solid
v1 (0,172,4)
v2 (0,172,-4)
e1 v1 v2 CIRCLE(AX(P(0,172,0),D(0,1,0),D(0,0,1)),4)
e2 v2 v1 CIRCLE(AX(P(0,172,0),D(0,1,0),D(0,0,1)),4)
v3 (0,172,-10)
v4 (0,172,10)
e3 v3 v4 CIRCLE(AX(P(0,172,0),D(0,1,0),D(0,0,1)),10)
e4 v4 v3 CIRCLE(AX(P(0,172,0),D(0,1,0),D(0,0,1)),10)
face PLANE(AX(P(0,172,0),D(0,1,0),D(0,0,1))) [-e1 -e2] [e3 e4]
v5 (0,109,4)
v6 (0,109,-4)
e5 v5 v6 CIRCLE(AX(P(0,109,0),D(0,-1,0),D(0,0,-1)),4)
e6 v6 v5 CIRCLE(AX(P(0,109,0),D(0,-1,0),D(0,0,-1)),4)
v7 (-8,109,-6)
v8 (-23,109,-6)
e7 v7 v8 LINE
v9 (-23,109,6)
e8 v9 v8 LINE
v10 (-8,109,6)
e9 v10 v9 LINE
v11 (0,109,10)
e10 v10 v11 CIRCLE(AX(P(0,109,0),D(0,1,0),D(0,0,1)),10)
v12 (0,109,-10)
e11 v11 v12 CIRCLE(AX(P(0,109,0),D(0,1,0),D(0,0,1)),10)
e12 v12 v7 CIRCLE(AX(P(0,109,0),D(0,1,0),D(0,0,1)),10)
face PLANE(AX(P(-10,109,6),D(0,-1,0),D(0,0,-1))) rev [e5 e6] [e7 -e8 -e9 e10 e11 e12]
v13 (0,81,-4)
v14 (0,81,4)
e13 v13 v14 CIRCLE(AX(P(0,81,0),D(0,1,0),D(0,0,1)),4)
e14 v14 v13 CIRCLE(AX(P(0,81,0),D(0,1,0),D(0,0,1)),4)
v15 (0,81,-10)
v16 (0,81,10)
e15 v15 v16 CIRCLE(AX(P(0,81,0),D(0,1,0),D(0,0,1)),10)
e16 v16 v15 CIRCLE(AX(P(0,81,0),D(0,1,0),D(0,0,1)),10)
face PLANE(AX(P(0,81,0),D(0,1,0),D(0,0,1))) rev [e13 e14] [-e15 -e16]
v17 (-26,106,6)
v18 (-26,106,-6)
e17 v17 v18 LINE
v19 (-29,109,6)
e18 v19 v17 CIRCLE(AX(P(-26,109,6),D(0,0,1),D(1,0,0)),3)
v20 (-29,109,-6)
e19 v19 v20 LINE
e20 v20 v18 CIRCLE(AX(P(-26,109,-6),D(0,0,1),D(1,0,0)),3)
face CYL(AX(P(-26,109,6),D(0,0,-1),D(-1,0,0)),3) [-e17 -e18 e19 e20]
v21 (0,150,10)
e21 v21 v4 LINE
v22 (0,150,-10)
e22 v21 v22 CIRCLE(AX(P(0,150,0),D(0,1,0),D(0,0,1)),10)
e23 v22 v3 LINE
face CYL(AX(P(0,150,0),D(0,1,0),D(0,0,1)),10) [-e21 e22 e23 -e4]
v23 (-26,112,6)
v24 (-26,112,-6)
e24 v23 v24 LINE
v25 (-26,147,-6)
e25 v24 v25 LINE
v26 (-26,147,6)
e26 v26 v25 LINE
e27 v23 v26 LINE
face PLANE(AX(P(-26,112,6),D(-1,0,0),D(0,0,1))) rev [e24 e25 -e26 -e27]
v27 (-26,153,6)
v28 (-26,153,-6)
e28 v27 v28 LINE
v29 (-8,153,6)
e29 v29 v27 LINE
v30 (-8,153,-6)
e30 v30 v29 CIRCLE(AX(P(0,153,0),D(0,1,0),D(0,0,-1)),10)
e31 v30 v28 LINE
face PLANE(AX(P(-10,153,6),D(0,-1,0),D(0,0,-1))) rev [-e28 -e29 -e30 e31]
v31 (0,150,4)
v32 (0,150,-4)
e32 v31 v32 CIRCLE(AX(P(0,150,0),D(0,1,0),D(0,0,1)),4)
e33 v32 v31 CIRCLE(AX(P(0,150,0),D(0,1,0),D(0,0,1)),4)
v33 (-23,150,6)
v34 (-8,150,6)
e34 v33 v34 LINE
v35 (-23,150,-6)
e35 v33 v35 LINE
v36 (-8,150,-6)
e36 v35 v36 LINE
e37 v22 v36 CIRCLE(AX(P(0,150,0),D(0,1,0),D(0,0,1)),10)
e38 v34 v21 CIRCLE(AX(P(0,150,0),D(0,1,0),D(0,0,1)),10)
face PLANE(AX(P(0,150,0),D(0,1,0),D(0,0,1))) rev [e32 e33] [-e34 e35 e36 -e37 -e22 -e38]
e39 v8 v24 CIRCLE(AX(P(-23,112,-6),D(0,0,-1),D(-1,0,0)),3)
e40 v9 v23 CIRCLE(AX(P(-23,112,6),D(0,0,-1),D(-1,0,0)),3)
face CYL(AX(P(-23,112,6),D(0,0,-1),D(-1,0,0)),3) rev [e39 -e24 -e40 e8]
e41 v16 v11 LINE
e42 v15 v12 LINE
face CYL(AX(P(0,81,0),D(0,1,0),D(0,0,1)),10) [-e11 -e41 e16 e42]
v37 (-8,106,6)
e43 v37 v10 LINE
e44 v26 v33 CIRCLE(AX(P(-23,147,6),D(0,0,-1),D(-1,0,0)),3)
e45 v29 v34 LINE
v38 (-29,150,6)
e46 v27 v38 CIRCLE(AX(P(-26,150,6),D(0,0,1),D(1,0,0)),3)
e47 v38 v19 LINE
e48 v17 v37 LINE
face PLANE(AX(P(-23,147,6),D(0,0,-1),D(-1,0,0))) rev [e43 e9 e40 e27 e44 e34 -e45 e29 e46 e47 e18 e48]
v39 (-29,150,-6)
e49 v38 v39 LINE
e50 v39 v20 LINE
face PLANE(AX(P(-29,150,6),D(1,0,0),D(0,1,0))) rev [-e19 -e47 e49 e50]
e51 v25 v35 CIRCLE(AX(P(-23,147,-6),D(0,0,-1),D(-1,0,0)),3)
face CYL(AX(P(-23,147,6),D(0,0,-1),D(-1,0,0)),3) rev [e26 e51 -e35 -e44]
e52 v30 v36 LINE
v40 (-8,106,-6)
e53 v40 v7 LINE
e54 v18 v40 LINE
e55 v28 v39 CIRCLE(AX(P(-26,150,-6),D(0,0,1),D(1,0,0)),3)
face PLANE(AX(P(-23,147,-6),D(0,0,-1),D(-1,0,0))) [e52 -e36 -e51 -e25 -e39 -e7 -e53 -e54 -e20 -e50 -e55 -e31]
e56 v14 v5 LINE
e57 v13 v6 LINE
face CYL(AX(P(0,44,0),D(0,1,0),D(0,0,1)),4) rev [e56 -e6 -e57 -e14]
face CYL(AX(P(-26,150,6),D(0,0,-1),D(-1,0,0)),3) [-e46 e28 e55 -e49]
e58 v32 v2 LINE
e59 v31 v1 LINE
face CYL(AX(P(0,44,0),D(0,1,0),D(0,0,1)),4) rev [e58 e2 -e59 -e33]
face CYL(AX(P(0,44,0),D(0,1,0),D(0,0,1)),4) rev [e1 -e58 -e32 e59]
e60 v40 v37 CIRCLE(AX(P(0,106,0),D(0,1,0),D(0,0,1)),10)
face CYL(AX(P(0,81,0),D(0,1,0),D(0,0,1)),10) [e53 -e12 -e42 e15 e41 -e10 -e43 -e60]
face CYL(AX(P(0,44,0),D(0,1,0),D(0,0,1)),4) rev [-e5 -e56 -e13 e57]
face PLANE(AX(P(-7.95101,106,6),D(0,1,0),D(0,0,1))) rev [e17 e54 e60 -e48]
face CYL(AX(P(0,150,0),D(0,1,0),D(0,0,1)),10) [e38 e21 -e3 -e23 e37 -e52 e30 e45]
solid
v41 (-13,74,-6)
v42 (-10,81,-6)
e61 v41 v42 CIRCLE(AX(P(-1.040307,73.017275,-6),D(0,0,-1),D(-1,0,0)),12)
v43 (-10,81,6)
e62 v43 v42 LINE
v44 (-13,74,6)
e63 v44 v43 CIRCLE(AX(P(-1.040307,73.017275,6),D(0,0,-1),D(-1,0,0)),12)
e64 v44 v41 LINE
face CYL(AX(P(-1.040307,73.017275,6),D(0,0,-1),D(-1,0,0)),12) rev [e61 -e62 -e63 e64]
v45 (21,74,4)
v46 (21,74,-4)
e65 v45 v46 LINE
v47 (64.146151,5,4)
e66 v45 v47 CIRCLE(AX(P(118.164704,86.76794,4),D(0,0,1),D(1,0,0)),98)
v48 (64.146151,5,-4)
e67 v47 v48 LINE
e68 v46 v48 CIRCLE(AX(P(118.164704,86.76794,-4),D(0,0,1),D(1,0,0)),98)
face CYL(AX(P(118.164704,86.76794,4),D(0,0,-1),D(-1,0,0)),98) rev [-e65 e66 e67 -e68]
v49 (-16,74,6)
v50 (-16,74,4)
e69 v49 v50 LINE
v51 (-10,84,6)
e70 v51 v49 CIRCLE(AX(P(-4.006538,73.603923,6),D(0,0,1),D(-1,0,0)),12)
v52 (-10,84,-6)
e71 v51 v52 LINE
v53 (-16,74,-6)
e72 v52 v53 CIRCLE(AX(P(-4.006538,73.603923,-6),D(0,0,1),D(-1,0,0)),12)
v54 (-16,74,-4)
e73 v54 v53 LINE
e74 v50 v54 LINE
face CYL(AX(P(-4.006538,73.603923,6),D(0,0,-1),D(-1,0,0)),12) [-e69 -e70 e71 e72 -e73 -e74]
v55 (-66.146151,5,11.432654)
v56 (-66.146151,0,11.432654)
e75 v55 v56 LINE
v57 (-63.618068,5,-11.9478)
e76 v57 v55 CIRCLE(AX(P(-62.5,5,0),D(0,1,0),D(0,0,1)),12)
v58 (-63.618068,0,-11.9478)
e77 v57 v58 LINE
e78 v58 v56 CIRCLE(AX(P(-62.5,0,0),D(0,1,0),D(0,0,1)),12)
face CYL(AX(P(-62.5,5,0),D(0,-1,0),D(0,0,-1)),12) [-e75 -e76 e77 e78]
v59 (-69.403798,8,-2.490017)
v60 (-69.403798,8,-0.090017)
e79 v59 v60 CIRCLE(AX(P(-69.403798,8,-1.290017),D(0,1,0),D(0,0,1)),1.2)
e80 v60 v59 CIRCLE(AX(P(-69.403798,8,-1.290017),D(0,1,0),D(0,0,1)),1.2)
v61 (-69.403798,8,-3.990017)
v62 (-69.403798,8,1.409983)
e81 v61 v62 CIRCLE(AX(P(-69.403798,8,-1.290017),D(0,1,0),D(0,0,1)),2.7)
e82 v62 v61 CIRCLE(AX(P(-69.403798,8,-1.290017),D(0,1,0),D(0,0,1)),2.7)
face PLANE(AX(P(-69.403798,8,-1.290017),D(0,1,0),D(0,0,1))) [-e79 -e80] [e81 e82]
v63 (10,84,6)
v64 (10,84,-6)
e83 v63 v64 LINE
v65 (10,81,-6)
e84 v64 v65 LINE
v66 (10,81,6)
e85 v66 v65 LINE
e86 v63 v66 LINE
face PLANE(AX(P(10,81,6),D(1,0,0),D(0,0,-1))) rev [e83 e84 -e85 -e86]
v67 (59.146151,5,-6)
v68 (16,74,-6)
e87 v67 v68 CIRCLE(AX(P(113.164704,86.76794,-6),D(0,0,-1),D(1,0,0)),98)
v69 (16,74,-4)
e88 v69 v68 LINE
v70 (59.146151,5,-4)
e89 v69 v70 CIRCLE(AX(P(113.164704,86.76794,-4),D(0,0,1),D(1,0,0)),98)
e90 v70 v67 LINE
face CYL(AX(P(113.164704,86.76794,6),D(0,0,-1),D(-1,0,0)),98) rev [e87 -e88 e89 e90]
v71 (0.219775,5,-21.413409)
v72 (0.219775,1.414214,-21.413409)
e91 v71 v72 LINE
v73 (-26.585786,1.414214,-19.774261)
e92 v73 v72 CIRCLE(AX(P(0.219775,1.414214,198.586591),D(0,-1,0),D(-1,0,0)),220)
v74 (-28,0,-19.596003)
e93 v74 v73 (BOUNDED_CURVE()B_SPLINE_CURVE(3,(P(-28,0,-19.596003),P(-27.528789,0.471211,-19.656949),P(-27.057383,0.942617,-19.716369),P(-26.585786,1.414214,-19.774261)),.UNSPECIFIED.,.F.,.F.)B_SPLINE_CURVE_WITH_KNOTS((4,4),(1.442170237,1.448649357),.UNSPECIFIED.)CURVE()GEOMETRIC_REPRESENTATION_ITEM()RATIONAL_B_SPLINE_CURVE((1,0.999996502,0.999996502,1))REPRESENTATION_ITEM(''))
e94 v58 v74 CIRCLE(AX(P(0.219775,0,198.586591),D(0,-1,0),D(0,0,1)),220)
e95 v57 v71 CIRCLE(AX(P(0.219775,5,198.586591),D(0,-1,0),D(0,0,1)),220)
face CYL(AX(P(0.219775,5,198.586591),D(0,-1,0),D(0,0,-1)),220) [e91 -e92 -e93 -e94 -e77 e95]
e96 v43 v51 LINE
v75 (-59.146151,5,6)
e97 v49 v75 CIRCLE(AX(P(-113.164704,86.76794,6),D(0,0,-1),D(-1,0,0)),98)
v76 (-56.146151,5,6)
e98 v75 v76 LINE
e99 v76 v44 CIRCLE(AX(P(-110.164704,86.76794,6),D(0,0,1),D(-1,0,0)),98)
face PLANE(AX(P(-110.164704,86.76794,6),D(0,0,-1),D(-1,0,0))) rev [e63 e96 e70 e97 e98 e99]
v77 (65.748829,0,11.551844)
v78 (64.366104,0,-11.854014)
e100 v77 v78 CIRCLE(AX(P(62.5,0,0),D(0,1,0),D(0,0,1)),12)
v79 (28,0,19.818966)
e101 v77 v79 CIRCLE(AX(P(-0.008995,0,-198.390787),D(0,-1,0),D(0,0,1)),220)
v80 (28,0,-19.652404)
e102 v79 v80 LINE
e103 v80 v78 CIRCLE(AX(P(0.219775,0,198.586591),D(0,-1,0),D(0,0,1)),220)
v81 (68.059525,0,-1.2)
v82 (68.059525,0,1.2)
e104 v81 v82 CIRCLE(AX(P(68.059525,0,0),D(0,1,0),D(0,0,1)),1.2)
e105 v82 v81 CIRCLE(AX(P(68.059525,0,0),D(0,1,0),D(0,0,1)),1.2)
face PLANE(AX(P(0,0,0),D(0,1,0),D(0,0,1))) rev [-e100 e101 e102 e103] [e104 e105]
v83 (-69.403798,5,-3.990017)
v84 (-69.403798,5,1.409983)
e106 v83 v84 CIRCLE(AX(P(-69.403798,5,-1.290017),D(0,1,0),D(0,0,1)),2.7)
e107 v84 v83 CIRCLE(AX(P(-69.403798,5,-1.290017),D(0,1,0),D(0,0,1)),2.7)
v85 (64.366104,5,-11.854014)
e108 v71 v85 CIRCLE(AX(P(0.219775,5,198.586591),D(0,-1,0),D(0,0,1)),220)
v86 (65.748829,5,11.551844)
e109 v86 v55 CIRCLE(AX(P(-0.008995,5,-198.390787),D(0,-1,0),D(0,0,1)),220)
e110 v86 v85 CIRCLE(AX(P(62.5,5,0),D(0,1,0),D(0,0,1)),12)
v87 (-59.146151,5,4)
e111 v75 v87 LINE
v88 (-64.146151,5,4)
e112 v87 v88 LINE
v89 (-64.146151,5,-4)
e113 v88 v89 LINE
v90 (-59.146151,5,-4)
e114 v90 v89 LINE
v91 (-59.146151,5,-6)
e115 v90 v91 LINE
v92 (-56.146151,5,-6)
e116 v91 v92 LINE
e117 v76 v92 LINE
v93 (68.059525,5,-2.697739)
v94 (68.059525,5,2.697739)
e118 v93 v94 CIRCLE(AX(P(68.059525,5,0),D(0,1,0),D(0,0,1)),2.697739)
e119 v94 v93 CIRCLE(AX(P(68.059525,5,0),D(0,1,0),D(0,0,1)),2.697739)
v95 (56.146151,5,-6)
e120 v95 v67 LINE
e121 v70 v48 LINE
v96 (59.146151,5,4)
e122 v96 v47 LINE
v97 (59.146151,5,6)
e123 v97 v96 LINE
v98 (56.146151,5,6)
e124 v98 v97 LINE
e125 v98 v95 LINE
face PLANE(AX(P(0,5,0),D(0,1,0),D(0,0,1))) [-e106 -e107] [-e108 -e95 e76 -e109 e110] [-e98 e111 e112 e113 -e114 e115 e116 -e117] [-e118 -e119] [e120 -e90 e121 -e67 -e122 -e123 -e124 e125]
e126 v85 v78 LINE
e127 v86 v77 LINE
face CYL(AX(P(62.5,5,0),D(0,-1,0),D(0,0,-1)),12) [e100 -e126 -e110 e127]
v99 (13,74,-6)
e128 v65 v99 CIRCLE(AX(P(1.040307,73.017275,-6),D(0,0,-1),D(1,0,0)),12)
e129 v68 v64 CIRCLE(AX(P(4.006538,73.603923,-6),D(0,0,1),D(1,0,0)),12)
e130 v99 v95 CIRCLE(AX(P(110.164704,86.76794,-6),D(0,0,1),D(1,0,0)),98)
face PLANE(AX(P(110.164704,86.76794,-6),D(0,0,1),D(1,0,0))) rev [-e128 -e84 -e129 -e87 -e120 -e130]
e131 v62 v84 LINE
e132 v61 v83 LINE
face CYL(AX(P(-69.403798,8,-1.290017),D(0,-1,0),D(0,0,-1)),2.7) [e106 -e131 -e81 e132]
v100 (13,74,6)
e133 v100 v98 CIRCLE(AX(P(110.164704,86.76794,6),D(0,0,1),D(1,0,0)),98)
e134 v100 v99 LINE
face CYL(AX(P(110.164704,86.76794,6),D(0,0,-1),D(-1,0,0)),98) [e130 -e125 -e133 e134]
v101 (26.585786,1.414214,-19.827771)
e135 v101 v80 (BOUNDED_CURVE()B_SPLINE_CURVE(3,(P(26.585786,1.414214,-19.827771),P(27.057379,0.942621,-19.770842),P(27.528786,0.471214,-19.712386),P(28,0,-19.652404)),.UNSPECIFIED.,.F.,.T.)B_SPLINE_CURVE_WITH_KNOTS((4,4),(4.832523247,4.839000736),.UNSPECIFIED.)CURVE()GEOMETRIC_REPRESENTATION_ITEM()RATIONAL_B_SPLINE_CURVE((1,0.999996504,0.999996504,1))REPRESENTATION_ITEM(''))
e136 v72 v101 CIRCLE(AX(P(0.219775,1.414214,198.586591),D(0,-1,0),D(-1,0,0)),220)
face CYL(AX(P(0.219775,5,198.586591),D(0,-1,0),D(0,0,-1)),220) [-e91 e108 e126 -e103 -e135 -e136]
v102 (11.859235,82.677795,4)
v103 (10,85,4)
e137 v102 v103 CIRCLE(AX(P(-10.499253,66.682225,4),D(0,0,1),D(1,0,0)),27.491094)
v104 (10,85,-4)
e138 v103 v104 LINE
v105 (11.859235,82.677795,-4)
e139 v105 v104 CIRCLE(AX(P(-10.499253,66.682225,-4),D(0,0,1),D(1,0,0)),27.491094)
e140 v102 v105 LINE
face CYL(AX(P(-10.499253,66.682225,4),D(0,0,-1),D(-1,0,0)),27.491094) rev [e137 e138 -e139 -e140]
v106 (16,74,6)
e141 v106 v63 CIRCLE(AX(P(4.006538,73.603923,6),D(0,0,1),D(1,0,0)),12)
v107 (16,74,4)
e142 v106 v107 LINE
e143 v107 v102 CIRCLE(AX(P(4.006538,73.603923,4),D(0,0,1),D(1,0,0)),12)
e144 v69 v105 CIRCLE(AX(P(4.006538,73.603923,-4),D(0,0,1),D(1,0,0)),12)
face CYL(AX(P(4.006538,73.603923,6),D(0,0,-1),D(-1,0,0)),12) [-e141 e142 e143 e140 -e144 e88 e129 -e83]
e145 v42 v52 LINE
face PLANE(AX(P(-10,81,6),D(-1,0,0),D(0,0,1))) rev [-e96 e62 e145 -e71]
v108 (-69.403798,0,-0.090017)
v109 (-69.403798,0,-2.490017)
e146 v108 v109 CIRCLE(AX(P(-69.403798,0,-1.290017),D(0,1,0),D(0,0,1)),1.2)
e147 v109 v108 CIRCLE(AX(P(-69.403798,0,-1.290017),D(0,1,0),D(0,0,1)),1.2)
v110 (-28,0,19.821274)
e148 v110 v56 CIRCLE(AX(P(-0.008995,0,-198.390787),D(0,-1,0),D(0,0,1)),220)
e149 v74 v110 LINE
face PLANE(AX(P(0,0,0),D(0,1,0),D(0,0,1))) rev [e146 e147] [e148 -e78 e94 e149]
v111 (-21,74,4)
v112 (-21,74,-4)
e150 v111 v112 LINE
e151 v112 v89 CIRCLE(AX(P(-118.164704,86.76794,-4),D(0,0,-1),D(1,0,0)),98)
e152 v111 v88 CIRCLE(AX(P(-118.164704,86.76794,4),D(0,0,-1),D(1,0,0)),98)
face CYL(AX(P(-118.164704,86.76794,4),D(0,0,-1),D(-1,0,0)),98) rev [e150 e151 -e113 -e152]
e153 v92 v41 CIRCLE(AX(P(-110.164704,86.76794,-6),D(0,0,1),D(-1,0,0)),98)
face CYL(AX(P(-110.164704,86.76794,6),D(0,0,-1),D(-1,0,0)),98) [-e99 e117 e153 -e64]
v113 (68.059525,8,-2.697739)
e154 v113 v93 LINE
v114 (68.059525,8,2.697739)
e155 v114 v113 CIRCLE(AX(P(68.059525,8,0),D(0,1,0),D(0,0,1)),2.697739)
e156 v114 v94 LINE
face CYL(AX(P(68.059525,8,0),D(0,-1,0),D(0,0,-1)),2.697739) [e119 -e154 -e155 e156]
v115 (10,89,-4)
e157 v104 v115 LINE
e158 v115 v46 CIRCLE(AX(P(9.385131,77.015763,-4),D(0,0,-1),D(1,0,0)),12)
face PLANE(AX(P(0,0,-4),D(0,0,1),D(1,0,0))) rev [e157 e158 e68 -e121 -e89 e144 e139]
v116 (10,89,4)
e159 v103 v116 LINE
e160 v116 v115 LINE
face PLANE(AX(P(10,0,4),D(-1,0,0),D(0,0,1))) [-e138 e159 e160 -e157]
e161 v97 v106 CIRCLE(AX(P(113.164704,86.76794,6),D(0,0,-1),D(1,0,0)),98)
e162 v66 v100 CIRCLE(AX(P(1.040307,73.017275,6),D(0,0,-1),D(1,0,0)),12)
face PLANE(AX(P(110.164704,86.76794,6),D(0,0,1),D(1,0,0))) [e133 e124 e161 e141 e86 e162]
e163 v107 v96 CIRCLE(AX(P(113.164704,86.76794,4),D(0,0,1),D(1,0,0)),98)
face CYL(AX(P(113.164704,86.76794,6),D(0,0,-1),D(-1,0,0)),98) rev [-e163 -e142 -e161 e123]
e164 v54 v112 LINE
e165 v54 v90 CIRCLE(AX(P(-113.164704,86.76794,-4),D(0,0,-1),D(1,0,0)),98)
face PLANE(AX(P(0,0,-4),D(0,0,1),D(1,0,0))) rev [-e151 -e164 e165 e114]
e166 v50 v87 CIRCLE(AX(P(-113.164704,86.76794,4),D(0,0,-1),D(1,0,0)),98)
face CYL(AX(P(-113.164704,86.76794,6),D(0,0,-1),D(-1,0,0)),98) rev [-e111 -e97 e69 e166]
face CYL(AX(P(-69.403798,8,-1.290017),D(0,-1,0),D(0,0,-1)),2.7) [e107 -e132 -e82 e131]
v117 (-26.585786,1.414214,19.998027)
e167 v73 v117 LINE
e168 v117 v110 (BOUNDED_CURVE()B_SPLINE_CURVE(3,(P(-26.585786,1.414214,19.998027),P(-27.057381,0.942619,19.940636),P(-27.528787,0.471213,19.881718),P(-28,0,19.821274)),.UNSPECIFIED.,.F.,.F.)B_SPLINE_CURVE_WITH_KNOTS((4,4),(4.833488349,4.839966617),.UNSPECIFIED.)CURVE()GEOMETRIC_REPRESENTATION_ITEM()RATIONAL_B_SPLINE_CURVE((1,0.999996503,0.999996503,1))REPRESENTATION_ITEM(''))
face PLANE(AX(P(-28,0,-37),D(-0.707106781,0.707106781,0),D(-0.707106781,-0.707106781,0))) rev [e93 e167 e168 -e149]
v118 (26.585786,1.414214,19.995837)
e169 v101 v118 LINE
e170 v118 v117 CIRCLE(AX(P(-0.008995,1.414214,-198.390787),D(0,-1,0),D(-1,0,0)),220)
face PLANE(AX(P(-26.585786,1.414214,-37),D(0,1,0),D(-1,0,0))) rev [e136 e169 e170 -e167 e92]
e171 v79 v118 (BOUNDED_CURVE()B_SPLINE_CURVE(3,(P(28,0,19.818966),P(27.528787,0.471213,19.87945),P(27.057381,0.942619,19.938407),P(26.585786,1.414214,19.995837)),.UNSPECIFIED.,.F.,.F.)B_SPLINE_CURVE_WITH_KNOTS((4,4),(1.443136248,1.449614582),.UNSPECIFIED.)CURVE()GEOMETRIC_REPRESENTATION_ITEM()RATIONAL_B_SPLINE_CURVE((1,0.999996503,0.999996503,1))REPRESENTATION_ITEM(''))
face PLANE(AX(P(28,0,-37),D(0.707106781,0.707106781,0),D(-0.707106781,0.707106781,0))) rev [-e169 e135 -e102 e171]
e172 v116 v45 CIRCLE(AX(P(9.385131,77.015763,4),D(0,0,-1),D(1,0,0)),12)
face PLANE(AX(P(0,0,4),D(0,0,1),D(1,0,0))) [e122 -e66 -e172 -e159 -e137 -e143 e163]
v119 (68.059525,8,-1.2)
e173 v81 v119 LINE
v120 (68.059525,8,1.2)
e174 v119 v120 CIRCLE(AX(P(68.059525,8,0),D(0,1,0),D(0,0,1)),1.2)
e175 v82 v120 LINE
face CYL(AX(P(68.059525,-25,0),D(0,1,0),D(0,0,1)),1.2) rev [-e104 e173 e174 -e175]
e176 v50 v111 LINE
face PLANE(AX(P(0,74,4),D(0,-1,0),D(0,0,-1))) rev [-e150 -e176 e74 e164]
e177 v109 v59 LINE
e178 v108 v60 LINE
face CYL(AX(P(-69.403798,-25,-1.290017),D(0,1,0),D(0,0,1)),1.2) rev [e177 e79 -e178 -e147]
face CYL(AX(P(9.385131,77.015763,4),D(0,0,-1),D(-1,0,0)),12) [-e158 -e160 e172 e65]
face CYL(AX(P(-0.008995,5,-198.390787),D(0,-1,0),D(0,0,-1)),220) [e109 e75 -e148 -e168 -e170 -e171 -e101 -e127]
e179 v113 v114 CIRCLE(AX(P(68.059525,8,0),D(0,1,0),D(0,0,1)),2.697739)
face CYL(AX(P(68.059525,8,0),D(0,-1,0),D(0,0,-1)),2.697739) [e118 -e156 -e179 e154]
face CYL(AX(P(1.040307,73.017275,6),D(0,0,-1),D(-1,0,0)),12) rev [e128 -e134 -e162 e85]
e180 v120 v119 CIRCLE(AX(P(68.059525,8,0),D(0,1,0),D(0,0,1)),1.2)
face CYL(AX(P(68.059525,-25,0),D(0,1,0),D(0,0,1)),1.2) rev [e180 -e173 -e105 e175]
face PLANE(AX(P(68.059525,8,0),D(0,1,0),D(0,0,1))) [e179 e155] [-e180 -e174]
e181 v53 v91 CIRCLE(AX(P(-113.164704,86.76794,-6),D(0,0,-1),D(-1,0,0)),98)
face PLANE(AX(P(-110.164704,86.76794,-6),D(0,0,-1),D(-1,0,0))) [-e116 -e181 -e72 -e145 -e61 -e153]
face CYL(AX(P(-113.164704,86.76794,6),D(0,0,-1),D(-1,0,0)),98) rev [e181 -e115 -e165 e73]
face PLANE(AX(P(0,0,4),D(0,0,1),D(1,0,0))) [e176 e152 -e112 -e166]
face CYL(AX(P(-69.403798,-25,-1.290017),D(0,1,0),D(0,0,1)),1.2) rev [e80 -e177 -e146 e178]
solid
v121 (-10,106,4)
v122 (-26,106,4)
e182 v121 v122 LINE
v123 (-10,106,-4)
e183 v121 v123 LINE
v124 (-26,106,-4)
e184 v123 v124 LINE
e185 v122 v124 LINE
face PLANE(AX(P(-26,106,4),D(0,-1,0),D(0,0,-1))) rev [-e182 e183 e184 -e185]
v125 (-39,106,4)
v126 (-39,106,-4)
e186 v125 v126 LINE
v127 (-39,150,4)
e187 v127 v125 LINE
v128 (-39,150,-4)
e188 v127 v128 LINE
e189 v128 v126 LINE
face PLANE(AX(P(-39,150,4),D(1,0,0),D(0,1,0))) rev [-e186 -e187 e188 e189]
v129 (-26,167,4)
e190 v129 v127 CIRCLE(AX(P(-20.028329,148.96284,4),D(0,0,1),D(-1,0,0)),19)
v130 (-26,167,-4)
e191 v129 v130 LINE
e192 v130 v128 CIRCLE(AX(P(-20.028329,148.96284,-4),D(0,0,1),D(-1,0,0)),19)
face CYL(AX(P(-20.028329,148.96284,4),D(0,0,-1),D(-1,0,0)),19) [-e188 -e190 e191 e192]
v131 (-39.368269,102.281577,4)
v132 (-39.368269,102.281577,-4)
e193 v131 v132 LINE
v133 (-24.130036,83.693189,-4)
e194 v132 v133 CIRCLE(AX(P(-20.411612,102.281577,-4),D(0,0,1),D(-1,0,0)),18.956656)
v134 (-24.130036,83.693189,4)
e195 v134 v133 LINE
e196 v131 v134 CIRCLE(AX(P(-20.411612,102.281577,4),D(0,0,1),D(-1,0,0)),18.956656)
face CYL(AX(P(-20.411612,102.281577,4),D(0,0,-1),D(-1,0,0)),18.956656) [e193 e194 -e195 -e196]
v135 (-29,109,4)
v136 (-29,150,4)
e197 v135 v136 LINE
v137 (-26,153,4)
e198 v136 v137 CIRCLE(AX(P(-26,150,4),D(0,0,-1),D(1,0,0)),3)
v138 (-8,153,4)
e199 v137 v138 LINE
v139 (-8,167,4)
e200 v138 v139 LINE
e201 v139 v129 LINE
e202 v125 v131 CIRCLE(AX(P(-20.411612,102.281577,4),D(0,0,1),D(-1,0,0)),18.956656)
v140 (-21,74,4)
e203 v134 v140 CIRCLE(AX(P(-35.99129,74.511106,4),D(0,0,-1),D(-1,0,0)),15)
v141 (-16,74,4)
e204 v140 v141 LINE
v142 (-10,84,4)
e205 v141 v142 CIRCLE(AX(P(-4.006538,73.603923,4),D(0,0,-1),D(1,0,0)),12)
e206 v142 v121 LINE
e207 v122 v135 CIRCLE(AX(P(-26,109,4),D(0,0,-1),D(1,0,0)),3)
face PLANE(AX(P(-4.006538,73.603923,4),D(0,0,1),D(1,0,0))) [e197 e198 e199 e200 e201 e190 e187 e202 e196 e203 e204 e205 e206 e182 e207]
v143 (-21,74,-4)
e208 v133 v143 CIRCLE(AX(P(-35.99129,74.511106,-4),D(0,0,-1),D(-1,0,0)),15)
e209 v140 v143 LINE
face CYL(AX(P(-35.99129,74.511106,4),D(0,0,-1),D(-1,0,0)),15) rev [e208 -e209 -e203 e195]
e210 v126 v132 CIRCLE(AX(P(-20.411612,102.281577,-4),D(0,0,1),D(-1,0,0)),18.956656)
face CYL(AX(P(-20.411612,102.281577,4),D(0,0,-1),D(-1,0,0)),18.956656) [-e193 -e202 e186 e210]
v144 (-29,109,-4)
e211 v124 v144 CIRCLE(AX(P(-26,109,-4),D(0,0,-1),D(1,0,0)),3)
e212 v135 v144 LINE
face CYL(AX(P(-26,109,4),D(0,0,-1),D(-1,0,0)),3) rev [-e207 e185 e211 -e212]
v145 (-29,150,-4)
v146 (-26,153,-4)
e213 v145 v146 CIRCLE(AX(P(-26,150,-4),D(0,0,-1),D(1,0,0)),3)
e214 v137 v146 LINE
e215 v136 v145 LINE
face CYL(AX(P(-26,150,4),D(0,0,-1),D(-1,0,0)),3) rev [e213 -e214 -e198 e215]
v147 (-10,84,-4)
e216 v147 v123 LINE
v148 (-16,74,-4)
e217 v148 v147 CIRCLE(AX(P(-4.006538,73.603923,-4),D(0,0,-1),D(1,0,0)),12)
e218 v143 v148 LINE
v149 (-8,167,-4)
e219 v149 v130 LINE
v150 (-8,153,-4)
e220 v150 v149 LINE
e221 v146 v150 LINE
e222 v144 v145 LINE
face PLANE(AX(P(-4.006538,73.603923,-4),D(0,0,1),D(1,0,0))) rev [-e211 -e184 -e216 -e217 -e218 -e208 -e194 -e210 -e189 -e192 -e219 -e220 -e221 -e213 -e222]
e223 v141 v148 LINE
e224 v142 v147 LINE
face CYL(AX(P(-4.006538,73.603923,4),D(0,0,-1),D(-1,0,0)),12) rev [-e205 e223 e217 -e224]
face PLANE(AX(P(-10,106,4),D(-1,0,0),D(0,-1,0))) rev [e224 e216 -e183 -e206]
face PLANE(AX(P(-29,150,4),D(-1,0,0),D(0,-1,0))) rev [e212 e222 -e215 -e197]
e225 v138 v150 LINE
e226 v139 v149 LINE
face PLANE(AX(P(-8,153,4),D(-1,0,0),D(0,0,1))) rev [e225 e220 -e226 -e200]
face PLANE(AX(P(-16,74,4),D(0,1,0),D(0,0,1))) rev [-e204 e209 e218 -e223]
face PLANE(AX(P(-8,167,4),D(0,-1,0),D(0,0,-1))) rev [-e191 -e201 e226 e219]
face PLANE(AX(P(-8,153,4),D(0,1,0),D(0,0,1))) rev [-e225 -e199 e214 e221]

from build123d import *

# Parameters (mm, degrees)
BASE_PLATE_DEPTH             = 5
UPPER_PIVOT_BOSS_SKETCH_R    = 10
UPPER_PIVOT_BOSS_DEPTH       = 22
LOWER_PIVOT_BOSS_SKETCH_R    = 10
LOWER_PIVOT_BOSS_DEPTH       = 28
SUPPORT_LEGS_DEPTH           = 6
C_ARM_DEPTH                  = 6
LEG_RIBS_DEPTH               = 4
C_ARM_RIB_DEPTH              = 4
PIVOT_BORE_SKETCH_R          = 4
PIVOT_BORE_DEPTH             = 128
BASE_SCREW_BOSSES_SKETCH_R   = 2.697739099
BASE_SCREW_BOSSES_SKETCH_R_2 = 2.7
BASE_SCREW_BOSSES_DEPTH      = 3
BASE_SCREW_HOLES_SKETCH_R    = 1.2
BASE_SCREW_HOLES_DEPTH       = 33
PROFILE_TRIM_CUT_DEPTH       = 59


with BuildPart() as part:
    # Base Plate Sketch → Base Plate (new body)
    with BuildSketch(Plane(origin=(0, 0, 0), x_dir=(1, 0, 0), z_dir=(0, 1, 0))):
        with BuildLine():
            ThreePointArc((64.36610424, 11.854014297), (0.380988732, 21.413349806), (-63.618068043, 11.947799959))
            ThreePointArc((-63.618068043, 11.947799959), (-74.430459123, 1.290017486), (-66.146151353, -11.432654124))
            ThreePointArc((-66.146151353, -11.432654124), (-66.105249037, -11.445618349), (-66.064300627, -11.458436239))
            ThreePointArc((-66.064300627, -11.458436239), (-0.16489578, -21.609157542), (65.7488293, -11.551844363))
            ThreePointArc((65.7488293, -11.551844363), (74.479114791, 0.707678469), (64.36610424, 11.854014297))
        make_face()
    extrude(amount=BASE_PLATE_DEPTH)

    # Support Legs Sketch → Support Legs (add, symmetric)
    with BuildSketch(Plane.XY):
        with BuildLine():
            Line((-56.146151353, 5), (-59.146151353, 5))
            ThreePointArc((-59.146151353, 5), (-30.072320043, 34.809728437), (-16, 74))
            ThreePointArc((-16, 74), (-14.296453431, 79.777872059), (-10, 84))
            Line((-10, 84), (-10, 81))
            ThreePointArc((-10, 81), (-12.070047611, 77.744306119), (-13, 74))
            ThreePointArc((-13, 74), (-27.072320043, 34.809728437), (-56.146151353, 5))
        make_face()
        with BuildLine():
            Line((56.146151353, 5), (59.146151353, 5))
            ThreePointArc((59.146151353, 5), (30.072320043, 34.809728437), (16, 74))
            ThreePointArc((16, 74), (14.296453431, 79.777872059), (10, 84))
            Line((10, 84), (10, 81))
            ThreePointArc((10, 81), (12.070047611, 77.744306119), (13, 74))
            ThreePointArc((13, 74), (27.072320043, 34.809728437), (56.146151353, 5))
        make_face()
    extrude(amount=SUPPORT_LEGS_DEPTH, both=True)

    # Leg Ribs Sketch → Leg Ribs (add, symmetric)
    with BuildSketch(Plane.XY):
        with BuildLine():
            ThreePointArc((-16, 74), (-30.072320043, 34.809728437), (-59.146151353, 5))
            Line((-59.146151353, 5), (-64.146151353, 5))
            ThreePointArc((-64.146151353, 5), (-35.072320043, 34.809728437), (-21, 74))
            Line((-21, 74), (-16, 74))
        make_face()
        with BuildLine():
            ThreePointArc((16, 74), (30.072320043, 34.809728437), (59.146151353, 5))
            Line((59.146151353, 5), (64.146151353, 5))
            ThreePointArc((64.146151353, 5), (35.072320043, 34.809728437), (21, 74))
            ThreePointArc((21, 74), (19.061991309, 84.11212696), (10, 89))
            Line((10, 89), (10, 85))
            ThreePointArc((10, 85), (13.635056418, 79.84639441), (16, 74))
        make_face()
    extrude(amount=LEG_RIBS_DEPTH, both=True)

    # Base Screw Bosses Sketch → Base Screw Bosses (add)
    with BuildSketch(Plane(origin=(0, 5, 0), x_dir=(1, 0, 0), z_dir=(0, 1, 0))):
        with Locations(Location((68.059525022, 0, 0), (0, 0, 270))):
            Circle(BASE_SCREW_BOSSES_SKETCH_R)
        with Locations(Location((-69.403797915, 1.290017486, 0), (0, 0, 270))):
            Circle(BASE_SCREW_BOSSES_SKETCH_R_2)
    extrude(amount=BASE_SCREW_BOSSES_DEPTH)

    # Base Screw Holes Sketch → Base Screw Holes (cut)
    with BuildSketch(Plane(origin=(0, 8, 0), x_dir=(1, 0, 0), z_dir=(0, 1, 0))):
        with Locations(Location((68.059525022, 0, 0), (0, 0, 270))):
            Circle(BASE_SCREW_HOLES_SKETCH_R)
        with Locations(Location((-69.403797915, 1.290017486, 0), (0, 0, 270))):
            Circle(BASE_SCREW_HOLES_SKETCH_R)
    extrude(amount=-BASE_SCREW_HOLES_DEPTH, mode=Mode.SUBTRACT)

    # Profile Trim Sketch → Profile Trim Cut (cut)
    with BuildSketch(Plane.XY.offset(22)):
        Polygon((0, 0), (28, 0), (26.585786438, 1.414213562), (-26.585786438, 1.414213562), (-28, 0), align=None)
    extrude(amount=-PROFILE_TRIM_CUT_DEPTH, mode=Mode.SUBTRACT)


with BuildPart() as body_2:
    # Upper Pivot Boss Sketch → Upper Pivot Boss (new body)
    with BuildSketch(Plane(origin=(0, 172, 0), x_dir=(1, 0, 0), z_dir=(0, 1, 0))):
        with Locations(Location((0, 0, 0), (0, 0, 270))):
            Circle(UPPER_PIVOT_BOSS_SKETCH_R)
    extrude(amount=-UPPER_PIVOT_BOSS_DEPTH)



with BuildPart() as body_3:
    # Lower Pivot Boss Sketch → Lower Pivot Boss (new body)
    with BuildSketch(Plane(origin=(0, 109, 0), x_dir=(1, 0, 0), z_dir=(0, 1, 0))):
        with Locations(Location((0, 0, 0), (0, 0, 270))):
            Circle(LOWER_PIVOT_BOSS_SKETCH_R)
    extrude(amount=-LOWER_PIVOT_BOSS_DEPTH)


with BuildPart() as body_2_1:
    add(body_2.part)

    add(body_3.part)  # C-Arm merges body 3
    # C-Arm Sketch → C-Arm (add, symmetric)
    with BuildSketch(Plane.XY):
        with BuildLine():
            Line((-10, 153), (-26, 153))
            ThreePointArc((-26, 153), (-28.121320344, 152.121320344), (-29, 150))
            Line((-29, 150), (-29, 109))
            ThreePointArc((-29, 109), (-28.121320344, 106.878679656), (-26, 106))
            Line((-26, 106), (-10, 106))
            Line((-10, 106), (-7.9510102, 106))
            Line((-7.9510102, 106), (-7.9510102, 109))
            Line((-7.9510102, 109), (-10, 109))
            Line((-10, 109), (-23, 109))
            ThreePointArc((-23, 109), (-25.121320344, 109.878679656), (-26, 112))
            Line((-26, 112), (-26, 147))
            ThreePointArc((-26, 147), (-25.121320344, 149.121320344), (-23, 150))
            Line((-23, 150), (-10, 150))
            Line((-10, 150), (-7.9510102, 150))
            Line((-7.9510102, 150), (-7.9510102, 153))
            Line((-7.9510102, 153), (-10, 153))
        make_face()
    extrude(amount=C_ARM_DEPTH, both=True)

    # Pivot Bore Sketch → Pivot Bore (cut)
    with BuildSketch(Plane(origin=(0, 172, 0), x_dir=(1, 0, 0), z_dir=(0, 1, 0))):
        with Locations(Location((0, 0, 0), (0, 0, 270))):
            Circle(PIVOT_BORE_SKETCH_R)
    extrude(amount=-PIVOT_BORE_DEPTH, mode=Mode.SUBTRACT)


with BuildPart() as body_3_2:
    # C-Arm Rib Sketch → C-Arm Rib (new, symmetric)
    with BuildSketch(Plane.XY):
        with BuildLine():
            Line((-39, 150), (-39, 106))
            ThreePointArc((-39, 106), (-36.18490968, 91.76692418), (-24.130035795, 83.693189205))
            ThreePointArc((-24.130035795, 83.693189205), (-21.717038282, 79.120416406), (-21, 74))
            Line((-21, 74), (-16, 74))
            ThreePointArc((-16, 74), (-14.296453431, 79.777872059), (-10, 84))
            Line((-10, 84), (-10, 106))
            Line((-10, 106), (-26, 106))
            ThreePointArc((-26, 106), (-28.121320344, 106.878679656), (-29, 109))
            Line((-29, 109), (-29, 150))
            ThreePointArc((-29, 150), (-28.121320344, 152.121320344), (-26, 153))
            Line((-26, 153), (-8, 153))
            Line((-8, 153), (-8, 167))
            Line((-8, 167), (-26, 167))
            ThreePointArc((-26, 167), (-35.121127871, 160.504391901), (-39, 150))
        make_face()
    extrude(amount=C_ARM_RIB_DEPTH, both=True)


solid = Compound([part.part, body_2_1.part, body_3_2.part])
